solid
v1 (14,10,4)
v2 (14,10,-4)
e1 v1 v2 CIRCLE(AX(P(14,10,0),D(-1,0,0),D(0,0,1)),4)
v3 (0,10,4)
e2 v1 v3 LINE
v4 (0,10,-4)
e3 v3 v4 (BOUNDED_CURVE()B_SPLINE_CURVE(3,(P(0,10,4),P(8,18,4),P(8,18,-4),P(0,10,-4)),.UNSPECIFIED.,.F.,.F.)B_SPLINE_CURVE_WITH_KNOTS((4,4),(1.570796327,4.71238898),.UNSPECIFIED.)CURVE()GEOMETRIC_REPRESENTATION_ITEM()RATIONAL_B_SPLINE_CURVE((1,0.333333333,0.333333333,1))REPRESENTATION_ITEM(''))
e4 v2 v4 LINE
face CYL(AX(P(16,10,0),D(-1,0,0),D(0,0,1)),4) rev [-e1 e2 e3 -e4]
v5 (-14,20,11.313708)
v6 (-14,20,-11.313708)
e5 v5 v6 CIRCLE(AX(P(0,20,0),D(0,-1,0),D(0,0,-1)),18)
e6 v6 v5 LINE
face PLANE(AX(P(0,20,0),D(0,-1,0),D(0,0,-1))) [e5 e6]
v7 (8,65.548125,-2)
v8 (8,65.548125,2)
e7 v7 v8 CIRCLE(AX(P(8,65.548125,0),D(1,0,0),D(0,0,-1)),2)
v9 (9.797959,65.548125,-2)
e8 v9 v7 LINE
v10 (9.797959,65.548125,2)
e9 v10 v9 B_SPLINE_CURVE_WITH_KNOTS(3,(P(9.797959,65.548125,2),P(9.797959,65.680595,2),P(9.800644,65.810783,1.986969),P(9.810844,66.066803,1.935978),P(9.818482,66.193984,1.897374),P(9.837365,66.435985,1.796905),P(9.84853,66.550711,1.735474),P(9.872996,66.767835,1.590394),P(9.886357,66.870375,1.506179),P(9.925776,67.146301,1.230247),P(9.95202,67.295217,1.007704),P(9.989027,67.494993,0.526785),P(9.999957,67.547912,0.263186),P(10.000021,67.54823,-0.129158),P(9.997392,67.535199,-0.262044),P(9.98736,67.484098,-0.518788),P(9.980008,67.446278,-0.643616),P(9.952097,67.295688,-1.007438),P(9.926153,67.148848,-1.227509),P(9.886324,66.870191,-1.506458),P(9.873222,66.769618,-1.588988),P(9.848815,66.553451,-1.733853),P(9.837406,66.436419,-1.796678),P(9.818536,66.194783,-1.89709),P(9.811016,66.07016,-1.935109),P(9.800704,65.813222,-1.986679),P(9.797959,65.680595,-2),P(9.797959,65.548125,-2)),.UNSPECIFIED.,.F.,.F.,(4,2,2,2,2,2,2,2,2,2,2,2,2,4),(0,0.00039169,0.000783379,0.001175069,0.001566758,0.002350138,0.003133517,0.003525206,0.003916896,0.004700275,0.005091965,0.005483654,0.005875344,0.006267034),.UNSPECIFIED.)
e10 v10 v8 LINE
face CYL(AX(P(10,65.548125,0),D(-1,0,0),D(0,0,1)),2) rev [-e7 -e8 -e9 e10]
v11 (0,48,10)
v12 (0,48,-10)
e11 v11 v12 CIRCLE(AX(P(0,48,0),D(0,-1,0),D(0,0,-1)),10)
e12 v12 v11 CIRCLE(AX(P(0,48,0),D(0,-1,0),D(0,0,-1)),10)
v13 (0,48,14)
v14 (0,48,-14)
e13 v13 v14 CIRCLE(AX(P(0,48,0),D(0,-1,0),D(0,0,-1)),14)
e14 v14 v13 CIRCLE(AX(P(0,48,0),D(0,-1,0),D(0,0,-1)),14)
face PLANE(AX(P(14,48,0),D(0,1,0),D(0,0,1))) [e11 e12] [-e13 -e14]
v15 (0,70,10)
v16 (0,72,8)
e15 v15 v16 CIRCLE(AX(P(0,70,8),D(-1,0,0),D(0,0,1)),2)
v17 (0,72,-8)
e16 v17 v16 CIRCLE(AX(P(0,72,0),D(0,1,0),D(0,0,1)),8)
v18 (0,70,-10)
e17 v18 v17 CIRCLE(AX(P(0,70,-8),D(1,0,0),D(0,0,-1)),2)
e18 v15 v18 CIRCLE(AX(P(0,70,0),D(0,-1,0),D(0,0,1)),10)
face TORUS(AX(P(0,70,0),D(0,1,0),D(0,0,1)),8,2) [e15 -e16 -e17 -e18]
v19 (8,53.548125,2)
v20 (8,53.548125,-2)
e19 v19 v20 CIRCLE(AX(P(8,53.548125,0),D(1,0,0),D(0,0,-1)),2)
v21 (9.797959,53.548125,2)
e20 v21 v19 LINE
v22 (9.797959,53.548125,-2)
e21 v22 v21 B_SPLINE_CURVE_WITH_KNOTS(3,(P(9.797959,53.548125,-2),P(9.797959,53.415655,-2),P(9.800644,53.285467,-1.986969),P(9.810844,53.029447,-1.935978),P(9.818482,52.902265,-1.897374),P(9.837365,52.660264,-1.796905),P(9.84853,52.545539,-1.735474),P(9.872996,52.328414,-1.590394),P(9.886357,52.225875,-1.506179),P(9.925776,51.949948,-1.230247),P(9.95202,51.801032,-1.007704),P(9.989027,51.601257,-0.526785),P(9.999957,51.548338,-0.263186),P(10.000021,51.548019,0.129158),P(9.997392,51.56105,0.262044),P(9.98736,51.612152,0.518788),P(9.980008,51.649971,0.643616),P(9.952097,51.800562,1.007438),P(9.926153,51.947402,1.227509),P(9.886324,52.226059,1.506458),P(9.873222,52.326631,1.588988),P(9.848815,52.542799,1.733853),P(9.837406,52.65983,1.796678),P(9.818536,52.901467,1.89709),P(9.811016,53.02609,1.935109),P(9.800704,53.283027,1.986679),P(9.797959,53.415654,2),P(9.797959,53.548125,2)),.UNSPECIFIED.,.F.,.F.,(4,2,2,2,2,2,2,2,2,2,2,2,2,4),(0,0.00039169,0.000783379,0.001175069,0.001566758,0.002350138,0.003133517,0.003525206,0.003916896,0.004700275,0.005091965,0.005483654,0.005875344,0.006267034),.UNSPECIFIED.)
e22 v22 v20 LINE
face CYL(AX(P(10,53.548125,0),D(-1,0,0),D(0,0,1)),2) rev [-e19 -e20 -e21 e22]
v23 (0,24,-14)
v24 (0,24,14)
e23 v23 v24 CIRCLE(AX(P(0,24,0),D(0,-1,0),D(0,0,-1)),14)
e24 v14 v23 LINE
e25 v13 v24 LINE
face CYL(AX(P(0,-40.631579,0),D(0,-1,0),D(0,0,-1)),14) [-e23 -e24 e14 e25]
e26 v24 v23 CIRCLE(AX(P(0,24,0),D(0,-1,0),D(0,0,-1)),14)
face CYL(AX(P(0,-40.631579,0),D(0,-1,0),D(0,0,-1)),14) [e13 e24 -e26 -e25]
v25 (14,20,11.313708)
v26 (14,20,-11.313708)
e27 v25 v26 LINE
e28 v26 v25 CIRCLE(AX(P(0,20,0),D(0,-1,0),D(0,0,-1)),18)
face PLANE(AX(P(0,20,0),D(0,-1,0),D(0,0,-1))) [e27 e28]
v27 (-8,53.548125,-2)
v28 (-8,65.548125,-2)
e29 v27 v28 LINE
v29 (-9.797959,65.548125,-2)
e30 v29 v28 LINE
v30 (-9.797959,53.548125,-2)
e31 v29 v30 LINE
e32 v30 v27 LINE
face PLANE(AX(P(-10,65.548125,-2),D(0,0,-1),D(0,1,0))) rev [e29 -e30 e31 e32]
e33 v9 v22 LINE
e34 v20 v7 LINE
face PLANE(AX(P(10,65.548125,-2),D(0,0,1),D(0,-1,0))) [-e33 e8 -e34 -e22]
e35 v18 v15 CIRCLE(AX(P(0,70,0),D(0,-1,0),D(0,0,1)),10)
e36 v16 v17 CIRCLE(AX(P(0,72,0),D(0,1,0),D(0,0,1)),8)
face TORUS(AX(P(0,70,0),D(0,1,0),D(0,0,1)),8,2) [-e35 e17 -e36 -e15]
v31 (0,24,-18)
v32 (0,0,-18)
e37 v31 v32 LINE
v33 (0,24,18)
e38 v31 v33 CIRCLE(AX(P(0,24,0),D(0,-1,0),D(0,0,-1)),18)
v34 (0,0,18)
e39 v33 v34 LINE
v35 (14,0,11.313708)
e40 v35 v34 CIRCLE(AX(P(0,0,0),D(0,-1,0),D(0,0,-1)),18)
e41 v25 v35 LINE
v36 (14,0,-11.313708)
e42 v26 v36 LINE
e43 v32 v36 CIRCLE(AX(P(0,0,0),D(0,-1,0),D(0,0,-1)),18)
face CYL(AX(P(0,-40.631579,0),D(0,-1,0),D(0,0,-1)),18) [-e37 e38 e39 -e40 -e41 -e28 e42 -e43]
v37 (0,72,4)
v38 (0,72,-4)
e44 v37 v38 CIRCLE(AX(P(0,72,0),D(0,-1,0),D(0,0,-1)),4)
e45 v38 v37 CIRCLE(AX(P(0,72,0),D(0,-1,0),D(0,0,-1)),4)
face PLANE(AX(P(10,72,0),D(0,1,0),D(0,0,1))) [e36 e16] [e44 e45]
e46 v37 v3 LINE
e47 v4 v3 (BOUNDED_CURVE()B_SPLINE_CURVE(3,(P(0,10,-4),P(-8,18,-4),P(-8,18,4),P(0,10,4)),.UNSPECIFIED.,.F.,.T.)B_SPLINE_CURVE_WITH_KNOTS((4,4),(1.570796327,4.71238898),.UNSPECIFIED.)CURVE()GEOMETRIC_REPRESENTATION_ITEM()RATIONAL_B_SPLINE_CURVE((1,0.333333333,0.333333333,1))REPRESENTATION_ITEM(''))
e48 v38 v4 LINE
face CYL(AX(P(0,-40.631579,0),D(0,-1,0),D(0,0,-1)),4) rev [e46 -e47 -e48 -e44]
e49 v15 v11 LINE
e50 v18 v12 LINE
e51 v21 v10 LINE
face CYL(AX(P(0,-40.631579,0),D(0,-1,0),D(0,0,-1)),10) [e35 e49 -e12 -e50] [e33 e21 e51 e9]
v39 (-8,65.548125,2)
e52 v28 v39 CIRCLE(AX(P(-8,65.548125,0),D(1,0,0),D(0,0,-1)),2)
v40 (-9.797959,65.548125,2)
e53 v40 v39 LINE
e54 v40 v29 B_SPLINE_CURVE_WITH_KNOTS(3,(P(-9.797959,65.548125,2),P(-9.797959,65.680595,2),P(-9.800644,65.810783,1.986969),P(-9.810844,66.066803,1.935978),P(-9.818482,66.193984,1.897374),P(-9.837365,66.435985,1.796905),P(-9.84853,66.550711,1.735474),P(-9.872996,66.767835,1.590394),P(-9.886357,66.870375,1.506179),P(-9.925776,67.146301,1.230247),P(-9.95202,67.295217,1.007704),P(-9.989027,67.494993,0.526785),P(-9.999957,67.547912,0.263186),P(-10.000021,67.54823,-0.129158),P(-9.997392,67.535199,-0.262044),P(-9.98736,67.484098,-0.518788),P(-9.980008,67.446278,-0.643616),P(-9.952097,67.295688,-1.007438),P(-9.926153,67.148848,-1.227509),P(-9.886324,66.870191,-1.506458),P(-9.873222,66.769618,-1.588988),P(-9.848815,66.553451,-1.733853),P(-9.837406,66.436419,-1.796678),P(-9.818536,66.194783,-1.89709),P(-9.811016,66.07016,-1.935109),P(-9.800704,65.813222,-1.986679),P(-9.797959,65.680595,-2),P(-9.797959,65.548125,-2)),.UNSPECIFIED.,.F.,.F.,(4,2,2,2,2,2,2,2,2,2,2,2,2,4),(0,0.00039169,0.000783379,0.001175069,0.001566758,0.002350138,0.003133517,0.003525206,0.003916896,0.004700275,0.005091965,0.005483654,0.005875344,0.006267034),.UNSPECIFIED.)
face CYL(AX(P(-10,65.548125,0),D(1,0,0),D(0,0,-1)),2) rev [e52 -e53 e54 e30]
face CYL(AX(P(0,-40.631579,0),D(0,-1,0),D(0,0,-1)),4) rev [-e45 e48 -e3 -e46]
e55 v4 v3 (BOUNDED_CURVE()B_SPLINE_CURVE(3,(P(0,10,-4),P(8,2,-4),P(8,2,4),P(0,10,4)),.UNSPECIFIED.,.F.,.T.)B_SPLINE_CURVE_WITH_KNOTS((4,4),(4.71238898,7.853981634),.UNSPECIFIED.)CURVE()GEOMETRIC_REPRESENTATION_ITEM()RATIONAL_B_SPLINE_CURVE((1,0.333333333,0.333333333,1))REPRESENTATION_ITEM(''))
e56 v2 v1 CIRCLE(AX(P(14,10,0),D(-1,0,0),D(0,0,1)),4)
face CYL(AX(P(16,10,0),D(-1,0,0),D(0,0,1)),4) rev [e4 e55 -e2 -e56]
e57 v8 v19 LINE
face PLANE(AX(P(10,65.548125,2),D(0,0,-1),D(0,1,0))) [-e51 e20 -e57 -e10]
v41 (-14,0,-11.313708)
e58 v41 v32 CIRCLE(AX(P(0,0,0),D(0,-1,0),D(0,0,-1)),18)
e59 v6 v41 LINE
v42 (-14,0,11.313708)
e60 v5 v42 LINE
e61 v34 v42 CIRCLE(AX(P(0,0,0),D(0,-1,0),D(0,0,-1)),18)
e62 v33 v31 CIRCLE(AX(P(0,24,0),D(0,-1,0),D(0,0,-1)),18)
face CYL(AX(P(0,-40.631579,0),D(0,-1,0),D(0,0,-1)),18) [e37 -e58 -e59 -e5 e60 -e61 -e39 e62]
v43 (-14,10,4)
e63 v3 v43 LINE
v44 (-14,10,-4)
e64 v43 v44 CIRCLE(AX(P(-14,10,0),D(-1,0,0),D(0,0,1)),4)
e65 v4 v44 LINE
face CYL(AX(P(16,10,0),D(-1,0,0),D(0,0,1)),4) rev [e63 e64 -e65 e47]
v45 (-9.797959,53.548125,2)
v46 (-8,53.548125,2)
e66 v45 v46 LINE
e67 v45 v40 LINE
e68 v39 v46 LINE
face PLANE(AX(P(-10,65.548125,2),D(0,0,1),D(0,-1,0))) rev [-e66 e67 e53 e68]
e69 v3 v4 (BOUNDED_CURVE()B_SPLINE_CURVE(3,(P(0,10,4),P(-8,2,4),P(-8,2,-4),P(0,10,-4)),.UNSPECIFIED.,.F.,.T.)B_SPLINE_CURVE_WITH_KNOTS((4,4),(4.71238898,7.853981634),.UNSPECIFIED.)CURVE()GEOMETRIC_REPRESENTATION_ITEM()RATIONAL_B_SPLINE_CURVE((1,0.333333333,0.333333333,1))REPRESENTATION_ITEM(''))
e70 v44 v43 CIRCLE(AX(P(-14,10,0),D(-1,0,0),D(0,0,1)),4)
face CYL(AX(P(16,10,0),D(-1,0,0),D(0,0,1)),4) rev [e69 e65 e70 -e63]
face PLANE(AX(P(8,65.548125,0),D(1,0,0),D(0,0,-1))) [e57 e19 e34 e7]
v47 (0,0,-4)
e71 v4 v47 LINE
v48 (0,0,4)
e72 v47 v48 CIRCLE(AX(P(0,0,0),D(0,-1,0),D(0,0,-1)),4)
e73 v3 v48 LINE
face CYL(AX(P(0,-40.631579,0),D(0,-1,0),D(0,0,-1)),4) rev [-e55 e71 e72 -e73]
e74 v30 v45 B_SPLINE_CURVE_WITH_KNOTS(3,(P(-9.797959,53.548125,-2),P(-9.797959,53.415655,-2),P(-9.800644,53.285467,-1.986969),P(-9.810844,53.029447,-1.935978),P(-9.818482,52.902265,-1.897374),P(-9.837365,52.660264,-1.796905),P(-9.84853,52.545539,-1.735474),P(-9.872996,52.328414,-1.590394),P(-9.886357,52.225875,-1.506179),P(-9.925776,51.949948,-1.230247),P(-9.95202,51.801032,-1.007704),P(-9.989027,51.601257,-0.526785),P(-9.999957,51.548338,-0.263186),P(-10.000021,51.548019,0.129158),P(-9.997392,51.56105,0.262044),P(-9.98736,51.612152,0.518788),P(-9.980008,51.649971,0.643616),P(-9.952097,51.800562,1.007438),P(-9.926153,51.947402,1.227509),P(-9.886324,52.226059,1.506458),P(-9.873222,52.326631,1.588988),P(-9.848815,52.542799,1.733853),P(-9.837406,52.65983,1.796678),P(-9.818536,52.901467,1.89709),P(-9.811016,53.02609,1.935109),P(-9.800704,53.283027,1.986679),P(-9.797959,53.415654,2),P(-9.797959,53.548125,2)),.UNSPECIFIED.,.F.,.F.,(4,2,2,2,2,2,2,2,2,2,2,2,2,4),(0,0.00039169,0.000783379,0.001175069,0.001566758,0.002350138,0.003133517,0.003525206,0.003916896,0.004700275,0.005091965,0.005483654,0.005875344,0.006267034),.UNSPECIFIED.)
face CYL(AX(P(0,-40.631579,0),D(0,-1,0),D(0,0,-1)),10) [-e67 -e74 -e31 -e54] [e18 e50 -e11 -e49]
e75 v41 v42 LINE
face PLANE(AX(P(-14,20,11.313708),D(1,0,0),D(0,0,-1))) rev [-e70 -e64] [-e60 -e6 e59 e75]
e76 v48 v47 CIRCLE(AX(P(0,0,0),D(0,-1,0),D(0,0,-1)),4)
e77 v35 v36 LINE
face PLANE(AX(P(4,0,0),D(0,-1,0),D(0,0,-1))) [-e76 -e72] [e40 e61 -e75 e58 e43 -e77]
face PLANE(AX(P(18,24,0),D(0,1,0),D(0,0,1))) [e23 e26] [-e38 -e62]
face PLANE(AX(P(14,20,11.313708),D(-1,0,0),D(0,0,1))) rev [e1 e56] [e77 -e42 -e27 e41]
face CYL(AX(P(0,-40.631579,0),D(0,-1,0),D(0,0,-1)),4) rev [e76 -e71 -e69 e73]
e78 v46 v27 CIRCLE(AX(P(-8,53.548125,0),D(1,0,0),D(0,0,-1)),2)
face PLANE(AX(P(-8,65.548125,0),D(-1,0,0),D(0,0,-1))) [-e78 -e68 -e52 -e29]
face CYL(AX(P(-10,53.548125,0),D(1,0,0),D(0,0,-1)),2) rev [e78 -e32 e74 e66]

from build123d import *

# Parameters (mm, degrees)
BASE_START          = -20
BASE_FLAT_DEPTH     = 20
CROSS_HOLE_SKETCH_R = 4
CROSS_HOLE_8_DEPTH  = 30
EDGE_FILLET_R2_R    = 2
SLOT_2X16_DEPTH     = 2


with BuildPart() as part:
    # Shaft Profile Sketch → Stepped Shaft Body (revolve)
    with BuildSketch(Plane.XY, mode=Mode.PRIVATE) as stepped_shaft_body_sk:
        Polygon((4, 72), (4, 0), (18, 0), (18, 24), (14, 24), (14, 48), (10, 48), (10, 72), align=None)
    revolve(stepped_shaft_body_sk.sketch.rotate(Axis((0, -40.631578947, 0), (0, 1, 0)), 90), axis=Axis((0, -40.631578947, 0), (0, 1, 0)))

    # Base Flat Sketch → Base Flat (cut)
    with BuildSketch(Plane.XZ.offset(BASE_START)):
        with BuildLine():
            Line((-14, 11.313708499), (-14, -11.313708499))
            ThreePointArc((-14, -11.313708499), (-18, 0), (-14, 11.313708499))
        make_face()
        with BuildLine():
            Line((14, 11.313708499), (14, -11.313708499))
            ThreePointArc((14, -11.313708499), (18, 0), (14, 11.313708499))
        make_face()
    extrude(amount=BASE_FLAT_DEPTH, mode=Mode.SUBTRACT)

    # Cross Hole Sketch → Cross Hole Ø8 (cut)
    with BuildSketch(Plane.ZY.offset(14)):
        with Locations((0, 10)):
            Circle(CROSS_HOLE_SKETCH_R)
    extrude(amount=-CROSS_HOLE_8_DEPTH, mode=Mode.SUBTRACT)

    # Edge Fillet R2
    edge_fillet_r2_edges = [part.edges().sort_by_distance(p)[0] for p in [
        (0, 72, 10),
    ]]
    fillet(edge_fillet_r2_edges, radius=EDGE_FILLET_R2_R)

    # Slot Sketch → Slot 2x16 (cut)
    with BuildSketch(Plane(origin=(8, 0, 0), x_dir=(0, 0, -1), z_dir=(1, 0, 0))):
        with BuildLine():
            Line((2, 65.548124709), (2, 53.548124709))
            ThreePointArc((2, 53.548124709), (0, 51.548124709), (-2, 53.548124709))
            Line((-2, 53.548124709), (-2, 65.548124709))
            ThreePointArc((-2, 65.548124709), (0, 67.548124709), (2, 65.548124709))
        make_face()
    slot_2x16 = extrude(amount=SLOT_2X16_DEPTH, mode=Mode.SUBTRACT)

    # Slot Mirror: Slot 2x16 across plane
    add(slot_2x16.mirror(Plane(origin=(0, 0, 0), x_dir=(0, 0, 1), z_dir=(1, 0, 0))), mode=Mode.SUBTRACT)


solid = part.part
